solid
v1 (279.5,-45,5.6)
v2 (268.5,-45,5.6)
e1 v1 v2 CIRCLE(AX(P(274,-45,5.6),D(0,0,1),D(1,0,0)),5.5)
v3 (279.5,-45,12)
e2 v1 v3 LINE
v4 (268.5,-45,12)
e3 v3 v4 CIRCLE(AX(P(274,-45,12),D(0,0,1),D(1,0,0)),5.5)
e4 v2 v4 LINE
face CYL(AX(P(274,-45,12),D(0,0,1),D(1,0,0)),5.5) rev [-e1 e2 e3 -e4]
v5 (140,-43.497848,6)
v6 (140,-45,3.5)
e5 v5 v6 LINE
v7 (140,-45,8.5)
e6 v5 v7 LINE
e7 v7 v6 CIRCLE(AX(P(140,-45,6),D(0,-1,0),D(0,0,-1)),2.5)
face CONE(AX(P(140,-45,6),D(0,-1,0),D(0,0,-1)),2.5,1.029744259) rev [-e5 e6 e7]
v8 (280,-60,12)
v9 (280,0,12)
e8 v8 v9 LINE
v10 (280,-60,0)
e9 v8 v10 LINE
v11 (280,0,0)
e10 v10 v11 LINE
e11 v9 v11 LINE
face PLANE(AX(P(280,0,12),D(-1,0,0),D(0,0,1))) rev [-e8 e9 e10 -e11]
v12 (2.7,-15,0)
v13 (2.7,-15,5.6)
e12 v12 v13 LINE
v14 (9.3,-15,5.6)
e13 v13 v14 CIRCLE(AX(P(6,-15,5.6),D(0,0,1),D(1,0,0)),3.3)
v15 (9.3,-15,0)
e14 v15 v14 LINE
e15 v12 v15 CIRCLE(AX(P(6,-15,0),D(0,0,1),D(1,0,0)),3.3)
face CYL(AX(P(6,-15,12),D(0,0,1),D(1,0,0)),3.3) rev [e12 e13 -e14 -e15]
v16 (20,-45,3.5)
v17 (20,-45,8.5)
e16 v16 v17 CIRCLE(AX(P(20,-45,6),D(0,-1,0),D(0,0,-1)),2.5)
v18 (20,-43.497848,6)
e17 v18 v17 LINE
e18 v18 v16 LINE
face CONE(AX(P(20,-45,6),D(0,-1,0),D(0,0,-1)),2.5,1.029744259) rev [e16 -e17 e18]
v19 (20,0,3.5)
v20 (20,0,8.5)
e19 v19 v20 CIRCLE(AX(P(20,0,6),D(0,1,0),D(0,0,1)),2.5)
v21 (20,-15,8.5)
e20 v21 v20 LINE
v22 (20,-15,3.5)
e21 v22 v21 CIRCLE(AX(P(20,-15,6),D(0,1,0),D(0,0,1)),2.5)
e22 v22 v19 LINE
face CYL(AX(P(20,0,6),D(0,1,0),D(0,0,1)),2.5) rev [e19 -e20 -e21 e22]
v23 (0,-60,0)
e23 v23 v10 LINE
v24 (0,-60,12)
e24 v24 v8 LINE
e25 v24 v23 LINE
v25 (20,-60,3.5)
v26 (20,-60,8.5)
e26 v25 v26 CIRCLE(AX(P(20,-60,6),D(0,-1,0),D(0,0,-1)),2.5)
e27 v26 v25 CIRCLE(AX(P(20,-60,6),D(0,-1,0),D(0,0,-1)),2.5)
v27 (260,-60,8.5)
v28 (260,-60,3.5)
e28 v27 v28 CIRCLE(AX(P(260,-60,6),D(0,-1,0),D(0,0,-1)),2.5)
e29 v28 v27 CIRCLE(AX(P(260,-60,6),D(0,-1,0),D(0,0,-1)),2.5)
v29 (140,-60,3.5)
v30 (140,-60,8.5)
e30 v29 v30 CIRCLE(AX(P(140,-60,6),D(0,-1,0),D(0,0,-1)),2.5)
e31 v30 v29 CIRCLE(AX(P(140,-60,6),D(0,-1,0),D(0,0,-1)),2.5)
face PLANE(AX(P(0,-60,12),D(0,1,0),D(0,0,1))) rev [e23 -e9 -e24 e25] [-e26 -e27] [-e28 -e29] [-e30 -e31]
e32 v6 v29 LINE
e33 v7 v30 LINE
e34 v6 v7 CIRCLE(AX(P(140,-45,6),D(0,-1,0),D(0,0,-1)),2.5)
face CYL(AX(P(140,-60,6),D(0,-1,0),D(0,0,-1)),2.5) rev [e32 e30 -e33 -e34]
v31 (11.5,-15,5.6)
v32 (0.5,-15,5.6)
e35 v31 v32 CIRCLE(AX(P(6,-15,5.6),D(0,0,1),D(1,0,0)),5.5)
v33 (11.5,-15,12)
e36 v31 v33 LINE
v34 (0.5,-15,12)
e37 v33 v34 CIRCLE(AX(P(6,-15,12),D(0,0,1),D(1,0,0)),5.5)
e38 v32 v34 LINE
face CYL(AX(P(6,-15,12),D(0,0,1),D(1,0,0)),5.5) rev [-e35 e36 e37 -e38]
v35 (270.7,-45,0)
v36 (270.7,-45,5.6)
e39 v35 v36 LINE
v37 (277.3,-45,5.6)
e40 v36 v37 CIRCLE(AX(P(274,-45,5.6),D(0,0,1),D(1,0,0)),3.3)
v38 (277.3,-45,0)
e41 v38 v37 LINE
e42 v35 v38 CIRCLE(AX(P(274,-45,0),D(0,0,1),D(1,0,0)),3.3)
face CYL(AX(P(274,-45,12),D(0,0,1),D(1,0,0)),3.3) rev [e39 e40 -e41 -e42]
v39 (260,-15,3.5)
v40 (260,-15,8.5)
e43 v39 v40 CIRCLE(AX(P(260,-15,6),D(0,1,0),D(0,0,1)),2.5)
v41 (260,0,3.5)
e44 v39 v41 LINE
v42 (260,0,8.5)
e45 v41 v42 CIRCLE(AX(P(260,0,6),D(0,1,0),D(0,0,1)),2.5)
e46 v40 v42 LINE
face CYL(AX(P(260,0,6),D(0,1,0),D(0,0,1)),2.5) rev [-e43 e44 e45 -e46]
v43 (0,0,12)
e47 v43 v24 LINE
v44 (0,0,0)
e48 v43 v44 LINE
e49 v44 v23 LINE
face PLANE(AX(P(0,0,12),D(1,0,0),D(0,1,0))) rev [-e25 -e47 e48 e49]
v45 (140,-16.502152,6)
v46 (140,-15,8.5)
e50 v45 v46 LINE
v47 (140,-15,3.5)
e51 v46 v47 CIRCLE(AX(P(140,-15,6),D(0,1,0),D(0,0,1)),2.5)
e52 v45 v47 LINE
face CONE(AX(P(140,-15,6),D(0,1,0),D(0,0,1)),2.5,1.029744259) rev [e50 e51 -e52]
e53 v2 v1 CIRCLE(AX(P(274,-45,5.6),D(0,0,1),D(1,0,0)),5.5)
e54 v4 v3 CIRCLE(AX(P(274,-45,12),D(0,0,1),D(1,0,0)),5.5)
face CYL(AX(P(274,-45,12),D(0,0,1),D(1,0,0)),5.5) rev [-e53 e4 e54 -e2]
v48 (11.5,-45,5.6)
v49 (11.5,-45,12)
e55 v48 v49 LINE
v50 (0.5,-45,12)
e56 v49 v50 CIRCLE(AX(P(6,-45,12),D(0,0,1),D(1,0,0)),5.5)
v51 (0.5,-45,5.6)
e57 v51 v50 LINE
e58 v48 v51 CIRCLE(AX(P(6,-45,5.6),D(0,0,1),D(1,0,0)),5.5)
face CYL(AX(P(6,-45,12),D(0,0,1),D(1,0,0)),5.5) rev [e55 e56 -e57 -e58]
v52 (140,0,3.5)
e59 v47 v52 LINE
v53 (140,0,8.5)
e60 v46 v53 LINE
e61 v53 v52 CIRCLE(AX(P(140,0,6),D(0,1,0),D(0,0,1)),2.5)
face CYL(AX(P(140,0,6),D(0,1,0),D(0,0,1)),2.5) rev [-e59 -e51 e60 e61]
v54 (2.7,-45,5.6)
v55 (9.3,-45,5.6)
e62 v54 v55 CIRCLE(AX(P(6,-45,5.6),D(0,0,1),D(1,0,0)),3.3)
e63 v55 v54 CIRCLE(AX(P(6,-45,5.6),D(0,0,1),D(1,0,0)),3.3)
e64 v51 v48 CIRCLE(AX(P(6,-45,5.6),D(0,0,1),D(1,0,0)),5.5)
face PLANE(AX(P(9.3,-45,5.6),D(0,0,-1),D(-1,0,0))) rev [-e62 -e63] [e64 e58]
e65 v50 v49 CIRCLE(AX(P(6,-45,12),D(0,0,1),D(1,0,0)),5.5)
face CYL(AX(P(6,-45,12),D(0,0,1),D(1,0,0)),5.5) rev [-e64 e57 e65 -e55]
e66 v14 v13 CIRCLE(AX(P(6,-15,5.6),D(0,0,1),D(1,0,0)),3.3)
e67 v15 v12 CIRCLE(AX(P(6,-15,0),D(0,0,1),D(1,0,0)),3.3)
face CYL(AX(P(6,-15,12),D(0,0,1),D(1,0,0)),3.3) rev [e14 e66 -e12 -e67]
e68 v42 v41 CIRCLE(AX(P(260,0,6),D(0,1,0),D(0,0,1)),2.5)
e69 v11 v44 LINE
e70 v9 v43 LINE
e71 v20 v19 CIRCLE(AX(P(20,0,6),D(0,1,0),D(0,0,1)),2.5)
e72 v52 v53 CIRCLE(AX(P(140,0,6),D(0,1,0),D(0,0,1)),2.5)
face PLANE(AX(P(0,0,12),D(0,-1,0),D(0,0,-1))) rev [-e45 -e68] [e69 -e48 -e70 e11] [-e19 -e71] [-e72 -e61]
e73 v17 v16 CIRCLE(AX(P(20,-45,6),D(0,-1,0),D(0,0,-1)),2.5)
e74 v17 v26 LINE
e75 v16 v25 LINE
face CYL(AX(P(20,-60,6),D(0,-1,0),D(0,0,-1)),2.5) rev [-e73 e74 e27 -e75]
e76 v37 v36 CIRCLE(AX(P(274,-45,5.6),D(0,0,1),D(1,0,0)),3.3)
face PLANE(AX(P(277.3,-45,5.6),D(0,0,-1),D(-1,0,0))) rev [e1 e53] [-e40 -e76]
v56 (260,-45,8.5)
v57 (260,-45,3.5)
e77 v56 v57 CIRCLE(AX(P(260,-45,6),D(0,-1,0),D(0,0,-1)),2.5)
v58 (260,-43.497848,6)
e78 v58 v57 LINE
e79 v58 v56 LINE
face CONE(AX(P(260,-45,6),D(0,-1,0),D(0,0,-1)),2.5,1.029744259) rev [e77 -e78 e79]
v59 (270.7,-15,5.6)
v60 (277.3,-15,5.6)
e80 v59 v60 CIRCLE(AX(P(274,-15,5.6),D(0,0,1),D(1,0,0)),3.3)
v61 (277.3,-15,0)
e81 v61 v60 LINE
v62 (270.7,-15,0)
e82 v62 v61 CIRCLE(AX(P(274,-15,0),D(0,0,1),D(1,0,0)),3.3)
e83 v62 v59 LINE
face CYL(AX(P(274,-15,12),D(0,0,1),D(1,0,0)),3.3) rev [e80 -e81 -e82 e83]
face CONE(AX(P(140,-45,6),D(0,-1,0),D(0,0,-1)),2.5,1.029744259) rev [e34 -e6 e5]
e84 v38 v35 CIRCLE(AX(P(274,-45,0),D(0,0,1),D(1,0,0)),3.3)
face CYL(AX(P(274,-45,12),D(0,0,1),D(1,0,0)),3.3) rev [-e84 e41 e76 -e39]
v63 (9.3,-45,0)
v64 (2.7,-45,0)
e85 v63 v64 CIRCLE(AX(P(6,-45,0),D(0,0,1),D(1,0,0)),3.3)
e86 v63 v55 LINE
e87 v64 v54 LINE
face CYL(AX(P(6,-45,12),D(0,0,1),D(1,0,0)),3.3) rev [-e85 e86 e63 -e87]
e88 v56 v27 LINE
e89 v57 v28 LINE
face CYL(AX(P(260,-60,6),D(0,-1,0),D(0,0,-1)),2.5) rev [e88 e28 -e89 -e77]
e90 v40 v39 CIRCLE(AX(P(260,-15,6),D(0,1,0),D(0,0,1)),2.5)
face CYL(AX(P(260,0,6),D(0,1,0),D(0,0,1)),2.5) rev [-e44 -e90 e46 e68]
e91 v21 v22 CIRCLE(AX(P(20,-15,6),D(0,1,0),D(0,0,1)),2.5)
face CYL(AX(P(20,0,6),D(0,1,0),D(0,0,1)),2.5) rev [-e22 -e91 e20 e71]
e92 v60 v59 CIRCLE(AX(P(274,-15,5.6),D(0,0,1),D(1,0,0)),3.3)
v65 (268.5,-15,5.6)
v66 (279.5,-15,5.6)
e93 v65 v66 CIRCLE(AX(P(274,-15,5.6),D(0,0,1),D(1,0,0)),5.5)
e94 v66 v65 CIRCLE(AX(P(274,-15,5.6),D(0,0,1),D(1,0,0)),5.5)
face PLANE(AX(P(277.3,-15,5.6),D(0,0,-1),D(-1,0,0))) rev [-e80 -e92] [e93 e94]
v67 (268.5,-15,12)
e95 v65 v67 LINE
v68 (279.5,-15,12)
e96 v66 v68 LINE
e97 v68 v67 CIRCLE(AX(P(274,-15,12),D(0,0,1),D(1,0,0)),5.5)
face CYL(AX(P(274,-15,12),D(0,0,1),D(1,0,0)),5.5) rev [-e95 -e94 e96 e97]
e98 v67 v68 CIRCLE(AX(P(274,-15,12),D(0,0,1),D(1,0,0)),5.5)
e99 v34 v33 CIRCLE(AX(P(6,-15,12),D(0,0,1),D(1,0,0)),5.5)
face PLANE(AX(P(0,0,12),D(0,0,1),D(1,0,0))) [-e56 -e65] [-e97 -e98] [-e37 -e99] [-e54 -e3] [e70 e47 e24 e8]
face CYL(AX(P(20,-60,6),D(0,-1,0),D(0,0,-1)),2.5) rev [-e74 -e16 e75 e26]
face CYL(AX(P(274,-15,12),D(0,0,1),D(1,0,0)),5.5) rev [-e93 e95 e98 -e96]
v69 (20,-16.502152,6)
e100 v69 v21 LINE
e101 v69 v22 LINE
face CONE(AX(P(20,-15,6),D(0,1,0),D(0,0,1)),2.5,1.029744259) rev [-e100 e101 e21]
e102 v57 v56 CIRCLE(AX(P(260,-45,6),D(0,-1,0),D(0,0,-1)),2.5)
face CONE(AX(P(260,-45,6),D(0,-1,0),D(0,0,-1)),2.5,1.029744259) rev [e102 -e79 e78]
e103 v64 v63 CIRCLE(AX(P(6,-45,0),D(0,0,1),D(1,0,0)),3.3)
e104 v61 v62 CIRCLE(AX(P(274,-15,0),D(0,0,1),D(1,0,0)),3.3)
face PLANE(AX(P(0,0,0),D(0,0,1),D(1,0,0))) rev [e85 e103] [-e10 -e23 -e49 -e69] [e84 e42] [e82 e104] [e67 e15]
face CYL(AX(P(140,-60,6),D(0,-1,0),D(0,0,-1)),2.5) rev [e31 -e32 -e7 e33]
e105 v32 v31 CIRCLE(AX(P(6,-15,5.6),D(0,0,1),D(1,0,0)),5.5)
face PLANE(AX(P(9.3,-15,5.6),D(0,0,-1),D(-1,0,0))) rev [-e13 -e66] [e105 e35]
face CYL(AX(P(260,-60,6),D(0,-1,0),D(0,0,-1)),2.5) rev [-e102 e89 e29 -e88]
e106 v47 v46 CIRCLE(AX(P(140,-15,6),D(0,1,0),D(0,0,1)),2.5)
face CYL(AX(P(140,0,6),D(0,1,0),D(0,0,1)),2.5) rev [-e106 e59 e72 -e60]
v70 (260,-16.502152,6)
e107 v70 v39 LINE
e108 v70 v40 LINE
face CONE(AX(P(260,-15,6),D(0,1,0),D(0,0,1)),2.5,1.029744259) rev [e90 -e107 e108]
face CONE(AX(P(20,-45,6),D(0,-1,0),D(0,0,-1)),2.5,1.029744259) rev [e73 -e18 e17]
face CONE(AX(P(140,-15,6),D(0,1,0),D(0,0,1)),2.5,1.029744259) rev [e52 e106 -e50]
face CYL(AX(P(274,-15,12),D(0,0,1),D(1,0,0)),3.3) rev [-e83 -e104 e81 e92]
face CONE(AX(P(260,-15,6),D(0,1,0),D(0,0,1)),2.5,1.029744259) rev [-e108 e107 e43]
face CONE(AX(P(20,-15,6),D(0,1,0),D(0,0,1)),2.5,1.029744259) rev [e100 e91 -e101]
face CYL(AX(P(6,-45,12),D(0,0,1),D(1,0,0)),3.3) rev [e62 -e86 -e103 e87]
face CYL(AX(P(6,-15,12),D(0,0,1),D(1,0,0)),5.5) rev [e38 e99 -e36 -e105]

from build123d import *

# Parameters (mm, degrees)
SKETCH_1_W                     = 280
SKETCH_1_H                     = 60
EXTRUDE_1_DEPTH                = 12
HOLE_WIZARD_M6_1_D             = 5
HOLE_WIZARD_M6_1_DEPTH         = 15
HOLE_WIZARD_M6_1_TIP           = 1.502151548
HOLE_WIZARD_M6_2_D             = 5
HOLE_WIZARD_M6_2_DEPTH         = 15
HOLE_WIZARD_M6_2_TIP           = 1.502151548
HOLE_WIZARD_M6_1_2_D           = 6.6
HOLE_WIZARD_M6_1_2_CBORE_D     = 11
HOLE_WIZARD_M6_1_2_CBORE_DEPTH = 6.4


with BuildPart() as part:
    # 草图1 → 凸台-拉伸1 (new body)
    with BuildSketch(Plane.XY):
        with Locations((140, -30)):
            Rectangle(SKETCH_1_W, SKETCH_1_H)
    extrude(amount=EXTRUDE_1_DEPTH)

    # Hole Wizard M6 _1
    with Locations(Plane(origin=(0, 0, 0), x_dir=(1, 0, 0), z_dir=(0, 1, 0))):
        with Locations((260, -6), (140, -6), (20, -6)):
            Hole(HOLE_WIZARD_M6_1_D / 2, depth=HOLE_WIZARD_M6_1_DEPTH)
            with Locations((0, 0, -(HOLE_WIZARD_M6_1_DEPTH + HOLE_WIZARD_M6_1_TIP / 2))):  # 118° drill point
                Cone(0, HOLE_WIZARD_M6_1_D / 2, HOLE_WIZARD_M6_1_TIP, mode=Mode.SUBTRACT)

    # M6 螺纹孔2
    with Locations(Plane(origin=(0, -60, 0), x_dir=(-1, 0, 0), z_dir=(0, -1, 0))):
        with Locations((-260, -6), (-140, -6), (-20, -6)):
            Hole(HOLE_WIZARD_M6_2_D / 2, depth=HOLE_WIZARD_M6_2_DEPTH)
            with Locations((0, 0, -(HOLE_WIZARD_M6_2_DEPTH + HOLE_WIZARD_M6_2_TIP / 2))):  # 118° drill point
                Cone(0, HOLE_WIZARD_M6_2_D / 2, HOLE_WIZARD_M6_2_TIP, mode=Mode.SUBTRACT)

    # Hole Wizard M6 _1 2 (through all)
    with Locations(Plane.XY.offset(12)):
        with Locations((274, -45), (274, -15), (6, -45), (6, -15)):
            CounterBoreHole(HOLE_WIZARD_M6_1_2_D / 2, HOLE_WIZARD_M6_1_2_CBORE_D / 2, HOLE_WIZARD_M6_1_2_CBORE_DEPTH)


solid = part.part
